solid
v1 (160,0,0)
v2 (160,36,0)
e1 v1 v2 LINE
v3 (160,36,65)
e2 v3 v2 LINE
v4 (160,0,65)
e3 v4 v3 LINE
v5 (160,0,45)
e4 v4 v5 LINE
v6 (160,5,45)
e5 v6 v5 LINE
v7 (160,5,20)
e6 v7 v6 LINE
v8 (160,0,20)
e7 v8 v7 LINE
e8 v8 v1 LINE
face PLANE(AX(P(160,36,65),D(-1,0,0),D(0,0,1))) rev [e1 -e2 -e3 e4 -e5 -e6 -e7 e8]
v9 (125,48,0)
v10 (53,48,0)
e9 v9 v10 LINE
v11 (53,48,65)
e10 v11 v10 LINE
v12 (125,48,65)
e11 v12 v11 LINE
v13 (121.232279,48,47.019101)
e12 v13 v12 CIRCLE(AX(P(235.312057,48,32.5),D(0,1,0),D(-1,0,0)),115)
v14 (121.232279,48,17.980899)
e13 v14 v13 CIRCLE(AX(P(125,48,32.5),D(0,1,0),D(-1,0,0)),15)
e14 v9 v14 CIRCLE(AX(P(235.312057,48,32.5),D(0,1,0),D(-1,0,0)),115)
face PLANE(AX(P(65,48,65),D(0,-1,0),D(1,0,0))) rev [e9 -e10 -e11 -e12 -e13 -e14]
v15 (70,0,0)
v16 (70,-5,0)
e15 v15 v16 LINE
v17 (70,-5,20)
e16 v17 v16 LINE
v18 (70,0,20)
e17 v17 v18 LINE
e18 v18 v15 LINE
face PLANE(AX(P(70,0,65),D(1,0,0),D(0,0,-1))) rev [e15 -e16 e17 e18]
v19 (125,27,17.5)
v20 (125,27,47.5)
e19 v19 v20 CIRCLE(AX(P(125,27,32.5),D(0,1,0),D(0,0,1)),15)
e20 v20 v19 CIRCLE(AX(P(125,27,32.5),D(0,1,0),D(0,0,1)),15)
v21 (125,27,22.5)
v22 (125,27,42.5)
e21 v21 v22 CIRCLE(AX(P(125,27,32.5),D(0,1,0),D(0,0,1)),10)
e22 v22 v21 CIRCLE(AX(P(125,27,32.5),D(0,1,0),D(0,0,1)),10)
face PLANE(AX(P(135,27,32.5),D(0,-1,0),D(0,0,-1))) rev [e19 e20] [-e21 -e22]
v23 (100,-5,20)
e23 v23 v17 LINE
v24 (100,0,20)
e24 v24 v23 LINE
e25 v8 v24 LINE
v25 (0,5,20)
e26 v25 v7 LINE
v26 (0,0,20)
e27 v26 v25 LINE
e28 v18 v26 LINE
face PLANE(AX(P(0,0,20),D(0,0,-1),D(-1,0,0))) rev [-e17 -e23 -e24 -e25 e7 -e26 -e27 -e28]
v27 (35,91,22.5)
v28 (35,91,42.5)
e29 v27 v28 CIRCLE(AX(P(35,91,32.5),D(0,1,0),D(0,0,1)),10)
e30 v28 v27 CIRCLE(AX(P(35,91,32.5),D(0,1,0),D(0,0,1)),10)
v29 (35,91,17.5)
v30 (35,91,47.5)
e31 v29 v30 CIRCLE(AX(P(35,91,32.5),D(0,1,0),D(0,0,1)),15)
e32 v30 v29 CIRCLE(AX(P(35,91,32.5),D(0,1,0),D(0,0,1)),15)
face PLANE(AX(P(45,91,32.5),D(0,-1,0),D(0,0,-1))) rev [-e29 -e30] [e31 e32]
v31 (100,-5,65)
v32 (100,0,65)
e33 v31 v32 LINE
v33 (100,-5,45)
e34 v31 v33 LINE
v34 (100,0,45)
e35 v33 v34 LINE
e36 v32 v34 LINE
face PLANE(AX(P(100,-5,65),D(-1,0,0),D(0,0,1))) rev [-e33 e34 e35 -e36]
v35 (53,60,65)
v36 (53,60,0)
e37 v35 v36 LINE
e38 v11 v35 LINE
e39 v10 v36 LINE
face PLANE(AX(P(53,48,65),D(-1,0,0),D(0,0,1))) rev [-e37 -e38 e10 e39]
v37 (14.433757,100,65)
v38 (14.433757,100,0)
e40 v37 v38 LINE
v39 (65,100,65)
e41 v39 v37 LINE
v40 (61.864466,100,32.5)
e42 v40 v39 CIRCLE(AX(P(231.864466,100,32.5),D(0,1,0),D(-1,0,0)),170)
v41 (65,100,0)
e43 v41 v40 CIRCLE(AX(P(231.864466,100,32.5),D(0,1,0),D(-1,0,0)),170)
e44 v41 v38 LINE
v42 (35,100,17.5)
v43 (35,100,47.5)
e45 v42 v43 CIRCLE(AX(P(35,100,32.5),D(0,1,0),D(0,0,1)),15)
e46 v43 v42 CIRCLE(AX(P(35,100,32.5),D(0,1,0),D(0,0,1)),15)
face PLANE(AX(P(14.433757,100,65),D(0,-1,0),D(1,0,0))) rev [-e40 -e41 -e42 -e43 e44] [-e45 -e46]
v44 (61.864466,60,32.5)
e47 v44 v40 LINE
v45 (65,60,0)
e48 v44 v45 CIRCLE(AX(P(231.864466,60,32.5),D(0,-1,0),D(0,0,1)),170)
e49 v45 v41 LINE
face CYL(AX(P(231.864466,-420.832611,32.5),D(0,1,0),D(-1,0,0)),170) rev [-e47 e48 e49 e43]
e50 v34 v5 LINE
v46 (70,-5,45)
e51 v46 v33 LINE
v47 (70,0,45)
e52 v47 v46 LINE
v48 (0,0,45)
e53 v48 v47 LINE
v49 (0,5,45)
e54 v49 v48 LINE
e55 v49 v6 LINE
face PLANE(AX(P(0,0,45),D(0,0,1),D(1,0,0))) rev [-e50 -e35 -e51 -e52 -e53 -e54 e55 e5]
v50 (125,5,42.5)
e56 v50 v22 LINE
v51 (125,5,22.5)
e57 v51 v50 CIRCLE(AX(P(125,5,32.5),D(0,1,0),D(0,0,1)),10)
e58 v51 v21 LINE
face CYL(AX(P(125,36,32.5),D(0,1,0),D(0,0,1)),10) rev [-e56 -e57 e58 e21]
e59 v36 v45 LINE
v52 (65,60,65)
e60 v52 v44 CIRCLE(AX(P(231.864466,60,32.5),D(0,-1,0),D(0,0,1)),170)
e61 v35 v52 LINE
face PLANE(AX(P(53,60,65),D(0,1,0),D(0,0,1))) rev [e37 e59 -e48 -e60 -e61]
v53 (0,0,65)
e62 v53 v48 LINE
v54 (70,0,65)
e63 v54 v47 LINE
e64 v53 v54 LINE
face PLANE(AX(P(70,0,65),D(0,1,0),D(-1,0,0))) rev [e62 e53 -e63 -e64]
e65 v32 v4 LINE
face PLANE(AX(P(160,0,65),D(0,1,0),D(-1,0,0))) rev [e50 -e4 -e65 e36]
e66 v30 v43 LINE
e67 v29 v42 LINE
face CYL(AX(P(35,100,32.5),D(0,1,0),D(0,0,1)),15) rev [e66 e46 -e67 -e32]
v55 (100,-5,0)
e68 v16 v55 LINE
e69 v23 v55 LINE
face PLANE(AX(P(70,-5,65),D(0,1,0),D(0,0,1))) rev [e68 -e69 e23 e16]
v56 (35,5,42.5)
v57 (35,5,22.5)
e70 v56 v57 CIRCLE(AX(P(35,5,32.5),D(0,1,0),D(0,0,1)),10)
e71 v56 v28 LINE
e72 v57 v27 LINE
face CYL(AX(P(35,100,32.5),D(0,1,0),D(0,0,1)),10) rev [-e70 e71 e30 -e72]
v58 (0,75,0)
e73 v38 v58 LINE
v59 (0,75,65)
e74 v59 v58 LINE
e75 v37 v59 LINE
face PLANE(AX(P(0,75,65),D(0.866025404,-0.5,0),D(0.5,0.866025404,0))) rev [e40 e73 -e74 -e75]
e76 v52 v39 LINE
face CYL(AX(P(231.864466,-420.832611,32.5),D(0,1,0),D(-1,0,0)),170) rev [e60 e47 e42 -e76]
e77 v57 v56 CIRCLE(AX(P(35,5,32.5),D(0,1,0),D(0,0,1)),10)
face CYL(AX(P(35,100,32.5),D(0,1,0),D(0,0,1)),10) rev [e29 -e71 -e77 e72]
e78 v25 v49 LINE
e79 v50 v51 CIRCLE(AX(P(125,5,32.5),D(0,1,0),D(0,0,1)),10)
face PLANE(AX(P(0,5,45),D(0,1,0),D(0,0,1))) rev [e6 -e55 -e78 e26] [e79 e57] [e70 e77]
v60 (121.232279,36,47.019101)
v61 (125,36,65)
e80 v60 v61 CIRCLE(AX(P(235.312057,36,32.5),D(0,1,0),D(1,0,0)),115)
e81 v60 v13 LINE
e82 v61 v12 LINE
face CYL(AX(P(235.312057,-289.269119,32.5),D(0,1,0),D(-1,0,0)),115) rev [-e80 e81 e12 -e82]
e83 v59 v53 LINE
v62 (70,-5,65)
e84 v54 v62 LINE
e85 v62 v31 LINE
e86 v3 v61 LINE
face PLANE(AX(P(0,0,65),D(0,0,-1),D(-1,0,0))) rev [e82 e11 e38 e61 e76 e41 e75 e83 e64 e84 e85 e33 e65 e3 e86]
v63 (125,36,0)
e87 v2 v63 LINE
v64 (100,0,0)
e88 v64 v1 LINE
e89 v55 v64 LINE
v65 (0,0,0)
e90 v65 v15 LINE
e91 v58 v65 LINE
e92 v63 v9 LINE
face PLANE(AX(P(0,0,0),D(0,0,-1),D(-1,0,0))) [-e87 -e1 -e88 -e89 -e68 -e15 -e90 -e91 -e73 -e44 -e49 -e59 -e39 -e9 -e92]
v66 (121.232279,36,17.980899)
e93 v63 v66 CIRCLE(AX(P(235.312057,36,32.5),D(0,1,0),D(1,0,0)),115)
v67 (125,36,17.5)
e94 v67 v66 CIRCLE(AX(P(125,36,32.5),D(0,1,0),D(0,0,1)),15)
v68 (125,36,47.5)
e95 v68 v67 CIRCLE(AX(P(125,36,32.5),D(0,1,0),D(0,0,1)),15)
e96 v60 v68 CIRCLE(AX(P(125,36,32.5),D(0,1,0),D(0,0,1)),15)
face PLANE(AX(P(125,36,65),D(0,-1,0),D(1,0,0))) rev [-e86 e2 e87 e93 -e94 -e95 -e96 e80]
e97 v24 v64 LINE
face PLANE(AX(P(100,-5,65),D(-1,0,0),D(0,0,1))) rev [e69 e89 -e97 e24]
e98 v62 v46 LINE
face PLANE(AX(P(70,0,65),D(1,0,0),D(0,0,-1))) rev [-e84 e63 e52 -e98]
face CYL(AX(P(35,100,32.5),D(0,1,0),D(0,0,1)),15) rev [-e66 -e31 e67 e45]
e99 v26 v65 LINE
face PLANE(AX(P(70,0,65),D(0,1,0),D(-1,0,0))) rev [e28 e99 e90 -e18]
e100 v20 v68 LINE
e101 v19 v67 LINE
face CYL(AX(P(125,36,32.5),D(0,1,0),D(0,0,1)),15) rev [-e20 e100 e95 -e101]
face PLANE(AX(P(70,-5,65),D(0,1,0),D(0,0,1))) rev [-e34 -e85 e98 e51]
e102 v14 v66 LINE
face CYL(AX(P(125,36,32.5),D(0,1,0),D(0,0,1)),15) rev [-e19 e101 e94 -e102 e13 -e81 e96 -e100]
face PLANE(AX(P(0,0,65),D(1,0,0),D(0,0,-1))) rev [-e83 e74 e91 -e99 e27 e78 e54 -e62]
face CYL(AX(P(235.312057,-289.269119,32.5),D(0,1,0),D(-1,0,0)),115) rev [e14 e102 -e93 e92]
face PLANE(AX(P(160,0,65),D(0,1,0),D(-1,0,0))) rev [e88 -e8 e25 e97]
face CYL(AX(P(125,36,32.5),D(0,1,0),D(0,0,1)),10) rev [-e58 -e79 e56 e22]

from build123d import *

# Parameters (mm, degrees)
STEPPED_BLOCK_BODY_DEPTH         = 65
RELIEF_CUT_20X20_DEPTH           = 200.562020435
ARC_CUT_115_SKETCH_R             = 115
ARC_CUT_115_DEPTH                = 12
ARC_CUT_170_SKETCH_R             = 170
ARC_CUT_170_DEPTH                = 40
LOWER_C_BORE_HOLE_20_D           = 20
LOWER_C_BORE_HOLE_20_DEPTH       = 99.874921777
LOWER_C_BORE_HOLE_20_CBORE_D     = 30
LOWER_C_BORE_HOLE_20_CBORE_DEPTH = 9
HOLE_CLEARANCE_NOTCH_SKETCH_R    = 15
HOLE_CLEARANCE_NOTCH_DEPTH       = 12


with BuildPart() as part:
    # Stepped Profile Sketch → Stepped Block Body (new body)
    with BuildSketch(Plane.XY):
        Polygon((0, 0), (0, 75), (14.43375673, 100), (65, 100), (65, 60), (53, 60), (53, 48), (65, 48), (125, 48), (125, 36), (160, 36), (160, 0), (100, 0), (100, -5), (70, -5), (70, 0), align=None)
    extrude(amount=STEPPED_BLOCK_BODY_DEPTH)

    # Relief Cut Sketch → Relief Cut 20x20 (cut, through all)
    with BuildSketch(Plane(origin=(160, 0, 0), x_dir=(0, 0, -1), z_dir=(1, 0, 0))):
        Polygon((-45, 0), (-45, 5), (-20, 5), (-20, 0), (-20, -9.038328121), (-45, -9.038328121), align=None)
    extrude(amount=-RELIEF_CUT_20X20_DEPTH, mode=Mode.SUBTRACT)

    # Arc Cut 115 Sketch → Arc Cut 115 (cut)
    with BuildSketch(Plane(origin=(0, 48, 0), x_dir=(1, 0, 0), z_dir=(0, 1, 0))):
        with Locations((235.312057365, -32.5)):
            Circle(ARC_CUT_115_SKETCH_R)
    extrude(amount=-ARC_CUT_115_DEPTH, mode=Mode.SUBTRACT)

    # Arc Cut 170 Sketch → Arc Cut 170 (cut)
    with BuildSketch(Plane(origin=(0, 100, 0), x_dir=(1, 0, 0), z_dir=(0, 1, 0))):
        with Locations((231.86446596, -32.5)):
            Circle(ARC_CUT_170_SKETCH_R)
    extrude(amount=-ARC_CUT_170_DEPTH, mode=Mode.SUBTRACT)

    # Sketch11 → Upper C-Bore Hole Ø20 (revolve, cut)
    with BuildSketch(Plane(origin=(125, 36, 32.5), x_dir=(0, 0, 1), z_dir=(1, 0, 0))):
        Polygon((0, 0), (0, 99.874921777), (10, 99.874921777), (10, 9), (15, 9), (15, 0), align=None)
    revolve(axis=Axis((125, -74, 32.5), (0, 1, 0)), mode=Mode.SUBTRACT)

    # Lower C-Bore Hole Ø20
    with Locations(Plane(origin=(35, 100, 32.5), x_dir=(1, 0, 0), z_dir=(0, 1, 0))):
        with Locations((0, 0)):
            CounterBoreHole(LOWER_C_BORE_HOLE_20_D / 2, LOWER_C_BORE_HOLE_20_CBORE_D / 2, LOWER_C_BORE_HOLE_20_CBORE_DEPTH, depth=LOWER_C_BORE_HOLE_20_DEPTH)

    # Hole Clearance Notch Sketch → Hole Clearance Notch (cut)
    with BuildSketch(Plane(origin=(0, 48, 0), x_dir=(1, 0, 0), z_dir=(0, 1, 0))):
        with Locations(Location((125, -32.5, 0), (0, 0, 270))):
            Circle(HOLE_CLEARANCE_NOTCH_SKETCH_R)
    extrude(amount=-HOLE_CLEARANCE_NOTCH_DEPTH, mode=Mode.SUBTRACT)


solid = part.part
